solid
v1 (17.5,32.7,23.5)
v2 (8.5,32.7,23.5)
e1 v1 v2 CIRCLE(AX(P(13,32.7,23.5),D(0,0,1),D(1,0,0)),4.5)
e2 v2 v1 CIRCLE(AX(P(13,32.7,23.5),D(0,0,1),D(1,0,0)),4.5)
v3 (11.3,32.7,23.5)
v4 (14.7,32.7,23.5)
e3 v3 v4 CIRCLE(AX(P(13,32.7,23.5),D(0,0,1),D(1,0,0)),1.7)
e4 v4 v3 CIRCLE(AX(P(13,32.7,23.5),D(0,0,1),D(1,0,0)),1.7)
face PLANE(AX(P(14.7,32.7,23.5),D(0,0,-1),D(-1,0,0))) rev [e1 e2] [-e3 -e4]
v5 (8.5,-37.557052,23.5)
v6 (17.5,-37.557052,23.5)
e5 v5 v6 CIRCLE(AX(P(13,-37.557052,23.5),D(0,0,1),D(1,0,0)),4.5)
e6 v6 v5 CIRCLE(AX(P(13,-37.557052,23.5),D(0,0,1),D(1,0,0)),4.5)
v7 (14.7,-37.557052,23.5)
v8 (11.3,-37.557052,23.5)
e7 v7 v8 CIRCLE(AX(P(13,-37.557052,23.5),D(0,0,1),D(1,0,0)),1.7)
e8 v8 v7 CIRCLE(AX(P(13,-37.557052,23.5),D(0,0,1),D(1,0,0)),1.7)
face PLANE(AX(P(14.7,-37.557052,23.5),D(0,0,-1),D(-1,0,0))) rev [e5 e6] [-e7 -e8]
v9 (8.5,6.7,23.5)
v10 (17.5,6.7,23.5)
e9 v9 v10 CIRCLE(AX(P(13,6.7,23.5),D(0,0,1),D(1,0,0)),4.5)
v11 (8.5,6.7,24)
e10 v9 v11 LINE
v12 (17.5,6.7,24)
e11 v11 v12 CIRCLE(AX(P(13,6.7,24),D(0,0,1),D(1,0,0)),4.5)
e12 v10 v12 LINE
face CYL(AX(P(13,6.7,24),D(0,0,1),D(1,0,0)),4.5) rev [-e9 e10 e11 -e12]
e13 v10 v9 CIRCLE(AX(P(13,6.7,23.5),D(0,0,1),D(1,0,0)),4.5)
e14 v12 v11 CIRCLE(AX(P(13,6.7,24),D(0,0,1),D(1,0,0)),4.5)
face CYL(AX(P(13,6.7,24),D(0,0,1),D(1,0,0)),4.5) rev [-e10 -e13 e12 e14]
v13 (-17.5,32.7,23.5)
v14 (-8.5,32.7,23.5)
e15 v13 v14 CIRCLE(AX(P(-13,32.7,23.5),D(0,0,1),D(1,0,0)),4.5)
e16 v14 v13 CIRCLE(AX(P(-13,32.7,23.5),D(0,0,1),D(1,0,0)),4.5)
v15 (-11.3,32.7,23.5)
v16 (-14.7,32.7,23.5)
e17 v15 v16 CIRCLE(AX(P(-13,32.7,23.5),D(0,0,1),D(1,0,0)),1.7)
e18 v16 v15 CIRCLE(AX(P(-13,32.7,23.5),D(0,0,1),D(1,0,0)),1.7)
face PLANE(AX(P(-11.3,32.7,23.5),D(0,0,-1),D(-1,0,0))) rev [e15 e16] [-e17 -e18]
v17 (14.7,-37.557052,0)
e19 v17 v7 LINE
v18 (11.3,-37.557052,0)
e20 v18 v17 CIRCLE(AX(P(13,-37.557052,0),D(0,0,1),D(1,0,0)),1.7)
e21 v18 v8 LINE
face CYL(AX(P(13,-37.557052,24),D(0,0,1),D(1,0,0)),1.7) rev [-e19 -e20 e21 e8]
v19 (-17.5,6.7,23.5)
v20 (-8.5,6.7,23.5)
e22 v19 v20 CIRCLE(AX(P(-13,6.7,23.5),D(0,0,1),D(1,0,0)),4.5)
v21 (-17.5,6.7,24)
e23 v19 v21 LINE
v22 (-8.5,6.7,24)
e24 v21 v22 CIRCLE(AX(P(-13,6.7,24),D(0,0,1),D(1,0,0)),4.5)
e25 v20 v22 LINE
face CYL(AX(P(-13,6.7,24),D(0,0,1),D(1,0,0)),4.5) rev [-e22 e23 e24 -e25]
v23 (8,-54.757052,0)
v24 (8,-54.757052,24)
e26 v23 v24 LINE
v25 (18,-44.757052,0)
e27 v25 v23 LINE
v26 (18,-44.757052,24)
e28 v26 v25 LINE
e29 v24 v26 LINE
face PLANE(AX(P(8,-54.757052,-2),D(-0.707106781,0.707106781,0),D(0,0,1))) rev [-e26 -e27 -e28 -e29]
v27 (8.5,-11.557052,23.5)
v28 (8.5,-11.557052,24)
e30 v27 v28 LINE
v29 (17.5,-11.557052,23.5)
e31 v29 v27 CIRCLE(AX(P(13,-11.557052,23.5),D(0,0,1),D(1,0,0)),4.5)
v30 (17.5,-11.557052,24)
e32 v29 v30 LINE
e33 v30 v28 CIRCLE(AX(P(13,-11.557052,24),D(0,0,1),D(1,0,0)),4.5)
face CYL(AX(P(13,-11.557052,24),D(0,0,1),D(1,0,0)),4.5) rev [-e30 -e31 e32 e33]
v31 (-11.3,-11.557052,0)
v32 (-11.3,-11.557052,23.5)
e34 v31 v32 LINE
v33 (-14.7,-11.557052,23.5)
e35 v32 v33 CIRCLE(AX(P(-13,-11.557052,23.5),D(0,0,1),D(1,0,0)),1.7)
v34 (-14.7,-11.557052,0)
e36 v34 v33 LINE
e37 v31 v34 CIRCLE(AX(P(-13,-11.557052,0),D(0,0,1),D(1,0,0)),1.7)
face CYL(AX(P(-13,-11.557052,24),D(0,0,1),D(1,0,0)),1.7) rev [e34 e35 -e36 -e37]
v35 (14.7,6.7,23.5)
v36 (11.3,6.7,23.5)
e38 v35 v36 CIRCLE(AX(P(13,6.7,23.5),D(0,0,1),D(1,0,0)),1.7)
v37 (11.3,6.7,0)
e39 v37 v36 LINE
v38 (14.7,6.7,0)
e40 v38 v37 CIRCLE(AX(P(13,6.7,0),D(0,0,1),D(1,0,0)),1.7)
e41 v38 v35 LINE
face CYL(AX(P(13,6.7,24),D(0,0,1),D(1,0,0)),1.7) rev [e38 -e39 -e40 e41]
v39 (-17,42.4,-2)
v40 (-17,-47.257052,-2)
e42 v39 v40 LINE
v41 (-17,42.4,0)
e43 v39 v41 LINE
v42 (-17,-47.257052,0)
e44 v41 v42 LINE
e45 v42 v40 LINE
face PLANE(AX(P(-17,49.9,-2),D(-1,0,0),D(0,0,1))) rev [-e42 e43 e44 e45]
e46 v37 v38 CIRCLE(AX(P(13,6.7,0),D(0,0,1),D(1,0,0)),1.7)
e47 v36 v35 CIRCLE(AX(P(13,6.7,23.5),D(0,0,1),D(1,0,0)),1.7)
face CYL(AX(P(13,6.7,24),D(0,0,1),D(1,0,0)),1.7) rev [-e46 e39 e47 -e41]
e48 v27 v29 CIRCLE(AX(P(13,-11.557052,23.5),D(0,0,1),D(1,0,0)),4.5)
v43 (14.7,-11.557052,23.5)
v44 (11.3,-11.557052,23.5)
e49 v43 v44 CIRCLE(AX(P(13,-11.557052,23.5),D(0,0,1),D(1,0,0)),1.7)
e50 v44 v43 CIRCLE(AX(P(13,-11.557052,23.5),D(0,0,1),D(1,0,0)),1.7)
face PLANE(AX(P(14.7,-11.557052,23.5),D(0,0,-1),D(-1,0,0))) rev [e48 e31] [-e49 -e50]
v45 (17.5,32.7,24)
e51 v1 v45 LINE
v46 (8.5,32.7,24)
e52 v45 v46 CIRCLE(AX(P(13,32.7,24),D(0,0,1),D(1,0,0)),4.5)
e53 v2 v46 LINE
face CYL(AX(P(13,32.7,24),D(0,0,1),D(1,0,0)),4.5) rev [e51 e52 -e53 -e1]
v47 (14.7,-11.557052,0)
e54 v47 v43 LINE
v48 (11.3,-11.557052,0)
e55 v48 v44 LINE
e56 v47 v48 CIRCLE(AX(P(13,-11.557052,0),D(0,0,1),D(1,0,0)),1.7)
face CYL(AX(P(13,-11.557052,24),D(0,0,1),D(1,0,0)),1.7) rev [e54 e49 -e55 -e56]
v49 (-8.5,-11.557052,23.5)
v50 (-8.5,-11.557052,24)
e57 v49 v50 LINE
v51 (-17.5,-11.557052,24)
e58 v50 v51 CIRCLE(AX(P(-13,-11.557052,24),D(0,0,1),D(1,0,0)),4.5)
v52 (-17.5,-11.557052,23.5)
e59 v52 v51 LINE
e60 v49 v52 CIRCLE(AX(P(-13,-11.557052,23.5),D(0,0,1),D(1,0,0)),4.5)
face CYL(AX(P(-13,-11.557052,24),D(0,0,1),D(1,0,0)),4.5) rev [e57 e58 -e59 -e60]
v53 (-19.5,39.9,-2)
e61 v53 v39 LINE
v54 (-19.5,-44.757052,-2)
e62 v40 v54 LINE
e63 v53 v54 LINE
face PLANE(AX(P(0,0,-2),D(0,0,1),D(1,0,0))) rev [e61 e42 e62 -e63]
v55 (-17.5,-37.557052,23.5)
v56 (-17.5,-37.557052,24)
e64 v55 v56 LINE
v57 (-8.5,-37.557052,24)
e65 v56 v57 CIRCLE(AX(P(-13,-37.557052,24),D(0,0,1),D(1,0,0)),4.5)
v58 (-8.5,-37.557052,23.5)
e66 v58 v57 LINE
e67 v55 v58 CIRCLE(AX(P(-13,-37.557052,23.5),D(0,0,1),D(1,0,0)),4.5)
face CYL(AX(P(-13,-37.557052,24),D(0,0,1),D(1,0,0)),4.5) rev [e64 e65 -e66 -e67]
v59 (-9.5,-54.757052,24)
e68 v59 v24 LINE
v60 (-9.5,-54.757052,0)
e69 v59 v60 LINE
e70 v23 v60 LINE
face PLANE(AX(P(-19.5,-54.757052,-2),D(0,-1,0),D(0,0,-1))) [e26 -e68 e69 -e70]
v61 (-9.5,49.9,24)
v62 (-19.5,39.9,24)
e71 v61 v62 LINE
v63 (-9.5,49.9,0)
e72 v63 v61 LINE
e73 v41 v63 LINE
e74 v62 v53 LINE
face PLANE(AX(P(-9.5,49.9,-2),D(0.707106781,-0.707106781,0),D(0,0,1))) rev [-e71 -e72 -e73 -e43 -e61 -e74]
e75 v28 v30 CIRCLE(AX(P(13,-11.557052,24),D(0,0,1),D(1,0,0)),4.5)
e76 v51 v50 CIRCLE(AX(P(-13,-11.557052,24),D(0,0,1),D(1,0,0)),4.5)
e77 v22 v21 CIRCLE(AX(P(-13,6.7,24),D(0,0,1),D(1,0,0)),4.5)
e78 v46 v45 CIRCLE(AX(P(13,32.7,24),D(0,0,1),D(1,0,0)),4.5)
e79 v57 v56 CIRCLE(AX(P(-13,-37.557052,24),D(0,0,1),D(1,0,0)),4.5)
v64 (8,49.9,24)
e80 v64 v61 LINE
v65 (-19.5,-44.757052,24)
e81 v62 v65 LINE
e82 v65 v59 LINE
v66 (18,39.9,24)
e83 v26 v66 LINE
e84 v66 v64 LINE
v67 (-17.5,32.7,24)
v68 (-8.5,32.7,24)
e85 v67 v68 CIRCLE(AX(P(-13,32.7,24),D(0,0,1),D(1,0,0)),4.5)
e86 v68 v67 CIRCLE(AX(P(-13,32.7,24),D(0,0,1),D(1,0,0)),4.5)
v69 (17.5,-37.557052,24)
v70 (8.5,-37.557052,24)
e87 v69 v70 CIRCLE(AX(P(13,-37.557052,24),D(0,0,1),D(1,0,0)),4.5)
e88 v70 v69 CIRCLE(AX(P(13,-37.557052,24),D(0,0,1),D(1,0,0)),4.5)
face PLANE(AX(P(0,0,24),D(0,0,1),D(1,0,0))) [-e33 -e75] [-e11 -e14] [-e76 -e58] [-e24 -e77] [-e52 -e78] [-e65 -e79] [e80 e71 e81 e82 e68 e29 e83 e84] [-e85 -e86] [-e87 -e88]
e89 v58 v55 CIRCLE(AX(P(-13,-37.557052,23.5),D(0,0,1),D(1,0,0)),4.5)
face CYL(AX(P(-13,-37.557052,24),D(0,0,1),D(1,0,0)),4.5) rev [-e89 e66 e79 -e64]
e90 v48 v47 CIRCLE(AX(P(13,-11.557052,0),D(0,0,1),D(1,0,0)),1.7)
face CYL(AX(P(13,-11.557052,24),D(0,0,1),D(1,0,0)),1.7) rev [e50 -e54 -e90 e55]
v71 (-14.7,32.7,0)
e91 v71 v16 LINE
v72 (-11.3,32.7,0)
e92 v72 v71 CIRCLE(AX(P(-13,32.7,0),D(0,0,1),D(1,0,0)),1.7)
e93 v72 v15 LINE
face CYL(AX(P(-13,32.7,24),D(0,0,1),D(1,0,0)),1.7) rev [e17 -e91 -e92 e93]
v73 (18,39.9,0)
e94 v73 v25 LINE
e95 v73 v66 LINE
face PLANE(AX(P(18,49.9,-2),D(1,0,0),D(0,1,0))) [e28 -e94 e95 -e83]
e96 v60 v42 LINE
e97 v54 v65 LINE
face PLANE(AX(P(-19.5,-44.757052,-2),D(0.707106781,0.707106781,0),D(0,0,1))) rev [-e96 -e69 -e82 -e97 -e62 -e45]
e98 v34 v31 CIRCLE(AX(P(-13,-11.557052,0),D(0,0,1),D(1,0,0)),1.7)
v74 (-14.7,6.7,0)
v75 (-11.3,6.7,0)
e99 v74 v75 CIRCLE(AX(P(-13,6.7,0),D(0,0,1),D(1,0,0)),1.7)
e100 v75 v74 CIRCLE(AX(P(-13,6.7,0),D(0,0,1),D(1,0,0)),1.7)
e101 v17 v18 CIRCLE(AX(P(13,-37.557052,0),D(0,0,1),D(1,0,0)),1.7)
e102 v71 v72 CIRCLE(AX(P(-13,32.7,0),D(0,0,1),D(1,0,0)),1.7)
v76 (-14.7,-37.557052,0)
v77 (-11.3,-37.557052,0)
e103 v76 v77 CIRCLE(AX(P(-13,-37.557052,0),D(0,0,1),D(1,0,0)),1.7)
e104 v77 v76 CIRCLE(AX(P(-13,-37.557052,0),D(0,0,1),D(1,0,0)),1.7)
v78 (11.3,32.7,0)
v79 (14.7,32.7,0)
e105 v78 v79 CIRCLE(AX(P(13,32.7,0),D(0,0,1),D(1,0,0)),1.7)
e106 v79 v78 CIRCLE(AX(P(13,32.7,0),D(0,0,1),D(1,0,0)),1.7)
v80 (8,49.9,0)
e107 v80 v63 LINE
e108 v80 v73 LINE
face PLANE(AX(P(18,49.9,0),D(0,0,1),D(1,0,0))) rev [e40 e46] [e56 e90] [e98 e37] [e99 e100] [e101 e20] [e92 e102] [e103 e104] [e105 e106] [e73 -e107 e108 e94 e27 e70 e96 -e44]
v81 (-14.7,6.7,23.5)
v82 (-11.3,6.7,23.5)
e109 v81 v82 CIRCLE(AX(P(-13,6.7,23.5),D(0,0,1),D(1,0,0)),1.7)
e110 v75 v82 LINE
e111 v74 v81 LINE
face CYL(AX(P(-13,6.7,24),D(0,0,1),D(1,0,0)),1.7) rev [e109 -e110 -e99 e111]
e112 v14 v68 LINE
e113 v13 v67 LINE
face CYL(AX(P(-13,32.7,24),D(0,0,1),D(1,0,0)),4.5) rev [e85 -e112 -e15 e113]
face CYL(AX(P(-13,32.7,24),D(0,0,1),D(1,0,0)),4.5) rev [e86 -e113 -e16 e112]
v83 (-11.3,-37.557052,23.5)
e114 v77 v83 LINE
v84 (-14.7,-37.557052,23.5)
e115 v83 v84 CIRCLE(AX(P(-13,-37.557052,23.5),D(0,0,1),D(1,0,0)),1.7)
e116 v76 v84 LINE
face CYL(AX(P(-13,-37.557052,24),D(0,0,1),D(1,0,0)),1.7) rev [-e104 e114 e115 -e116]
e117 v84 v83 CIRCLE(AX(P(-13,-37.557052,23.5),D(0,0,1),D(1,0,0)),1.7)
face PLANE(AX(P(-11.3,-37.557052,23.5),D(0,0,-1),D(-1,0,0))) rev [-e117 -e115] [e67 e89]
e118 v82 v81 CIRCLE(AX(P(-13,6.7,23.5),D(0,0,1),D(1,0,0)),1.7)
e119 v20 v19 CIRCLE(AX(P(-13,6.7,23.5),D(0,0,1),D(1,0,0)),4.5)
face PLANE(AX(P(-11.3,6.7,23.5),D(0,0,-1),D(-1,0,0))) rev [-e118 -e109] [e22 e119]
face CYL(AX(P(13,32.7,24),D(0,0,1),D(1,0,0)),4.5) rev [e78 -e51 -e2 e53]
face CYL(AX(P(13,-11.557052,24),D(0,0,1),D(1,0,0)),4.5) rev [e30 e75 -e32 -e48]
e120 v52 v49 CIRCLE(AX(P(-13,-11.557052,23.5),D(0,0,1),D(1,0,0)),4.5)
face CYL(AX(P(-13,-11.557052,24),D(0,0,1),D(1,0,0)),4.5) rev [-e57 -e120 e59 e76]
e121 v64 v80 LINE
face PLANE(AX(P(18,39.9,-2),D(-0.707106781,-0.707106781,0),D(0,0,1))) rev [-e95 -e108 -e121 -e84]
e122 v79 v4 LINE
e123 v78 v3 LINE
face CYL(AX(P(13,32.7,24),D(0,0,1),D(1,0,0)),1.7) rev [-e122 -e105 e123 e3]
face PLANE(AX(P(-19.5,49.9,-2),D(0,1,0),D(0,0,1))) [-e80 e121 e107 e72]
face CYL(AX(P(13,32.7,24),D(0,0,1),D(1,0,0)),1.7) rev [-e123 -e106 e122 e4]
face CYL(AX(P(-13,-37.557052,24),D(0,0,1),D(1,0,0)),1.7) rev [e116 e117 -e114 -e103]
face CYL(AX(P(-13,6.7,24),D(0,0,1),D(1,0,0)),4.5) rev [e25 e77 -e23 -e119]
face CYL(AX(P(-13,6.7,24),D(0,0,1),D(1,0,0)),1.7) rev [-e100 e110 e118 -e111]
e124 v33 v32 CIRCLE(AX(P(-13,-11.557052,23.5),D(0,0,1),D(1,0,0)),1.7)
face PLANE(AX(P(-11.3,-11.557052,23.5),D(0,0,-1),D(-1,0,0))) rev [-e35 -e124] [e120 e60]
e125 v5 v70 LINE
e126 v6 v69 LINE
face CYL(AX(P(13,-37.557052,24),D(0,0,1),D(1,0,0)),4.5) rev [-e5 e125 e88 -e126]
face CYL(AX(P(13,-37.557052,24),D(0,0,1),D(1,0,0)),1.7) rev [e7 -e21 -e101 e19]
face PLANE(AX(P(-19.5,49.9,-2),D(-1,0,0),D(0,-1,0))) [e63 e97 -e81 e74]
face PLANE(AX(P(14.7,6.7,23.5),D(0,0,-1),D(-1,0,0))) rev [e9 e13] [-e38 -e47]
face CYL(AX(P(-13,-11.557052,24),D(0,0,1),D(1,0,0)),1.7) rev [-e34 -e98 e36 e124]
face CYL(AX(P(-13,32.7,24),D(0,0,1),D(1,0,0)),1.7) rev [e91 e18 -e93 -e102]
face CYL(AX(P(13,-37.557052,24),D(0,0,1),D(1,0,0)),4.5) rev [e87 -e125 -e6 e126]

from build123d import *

# Parameters (mm, degrees)
BOSS_EXTRUDE1_DEPTH                     = 24
BOSS_EXTRUDE1_DEPTH_BACK                = 2
SKETCH1_W                               = 37.5
SKETCH1_H                               = 104.65705171
SKETCH2_W                               = 35
SKETCH2_H                               = 2
CUT_EXTRUDE1_DEPTH                      = 110.129961388
CHAMFER1_SIZE                           = 10
CBORE_FOR_M3_HEX_HEAD_BOLT1_D           = 3.4
CBORE_FOR_M3_HEX_HEAD_BOLT1_CBORE_D     = 9
CBORE_FOR_M3_HEX_HEAD_BOLT1_CBORE_DEPTH = 0.5


with BuildPart() as part:
    # Sketch1 → Boss-Extrude1 (new, two sides: drawn at the far end of the back side and taken through both)
    with BuildSketch(Plane.XY.offset(-BOSS_EXTRUDE1_DEPTH_BACK)):
        with Locations((-0.75, -2.428525855)):
            Rectangle(SKETCH1_W, SKETCH1_H)
    extrude(amount=BOSS_EXTRUDE1_DEPTH + BOSS_EXTRUDE1_DEPTH_BACK)

    # Sketch2 → Cut-Extrude1 (cut, through all)
    with BuildSketch(Plane.XZ.offset(54.75705171)):
        with Locations((0.5, -1)):
            Rectangle(SKETCH2_W, SKETCH2_H)
    extrude(amount=-CUT_EXTRUDE1_DEPTH, mode=Mode.SUBTRACT)

    # Chamfer1
    chamfer1_edges = [part.edges().sort_by_distance(p)[0] for p in [
        (18, -54.75705171, 12),
        (-19.5, -54.75705171, 11),
        (18, 49.9, 12),
        (-19.5, 49.9, 11),
    ]]
    chamfer(chamfer1_edges, length=CHAMFER1_SIZE)

    # CBORE for M3 Hex Head Bolt1 (through all)
    with Locations(Plane.XY.offset(24)):
        with Locations((-13, 32.7), (13, 32.7), (13, 6.7), (-13, 6.7), (-13, -11.55705171), (13, -11.55705171), (13, -37.55705171), (-13, -37.55705171)):
            CounterBoreHole(CBORE_FOR_M3_HEX_HEAD_BOLT1_D / 2, CBORE_FOR_M3_HEX_HEAD_BOLT1_CBORE_D / 2, CBORE_FOR_M3_HEX_HEAD_BOLT1_CBORE_DEPTH)


solid = part.part
